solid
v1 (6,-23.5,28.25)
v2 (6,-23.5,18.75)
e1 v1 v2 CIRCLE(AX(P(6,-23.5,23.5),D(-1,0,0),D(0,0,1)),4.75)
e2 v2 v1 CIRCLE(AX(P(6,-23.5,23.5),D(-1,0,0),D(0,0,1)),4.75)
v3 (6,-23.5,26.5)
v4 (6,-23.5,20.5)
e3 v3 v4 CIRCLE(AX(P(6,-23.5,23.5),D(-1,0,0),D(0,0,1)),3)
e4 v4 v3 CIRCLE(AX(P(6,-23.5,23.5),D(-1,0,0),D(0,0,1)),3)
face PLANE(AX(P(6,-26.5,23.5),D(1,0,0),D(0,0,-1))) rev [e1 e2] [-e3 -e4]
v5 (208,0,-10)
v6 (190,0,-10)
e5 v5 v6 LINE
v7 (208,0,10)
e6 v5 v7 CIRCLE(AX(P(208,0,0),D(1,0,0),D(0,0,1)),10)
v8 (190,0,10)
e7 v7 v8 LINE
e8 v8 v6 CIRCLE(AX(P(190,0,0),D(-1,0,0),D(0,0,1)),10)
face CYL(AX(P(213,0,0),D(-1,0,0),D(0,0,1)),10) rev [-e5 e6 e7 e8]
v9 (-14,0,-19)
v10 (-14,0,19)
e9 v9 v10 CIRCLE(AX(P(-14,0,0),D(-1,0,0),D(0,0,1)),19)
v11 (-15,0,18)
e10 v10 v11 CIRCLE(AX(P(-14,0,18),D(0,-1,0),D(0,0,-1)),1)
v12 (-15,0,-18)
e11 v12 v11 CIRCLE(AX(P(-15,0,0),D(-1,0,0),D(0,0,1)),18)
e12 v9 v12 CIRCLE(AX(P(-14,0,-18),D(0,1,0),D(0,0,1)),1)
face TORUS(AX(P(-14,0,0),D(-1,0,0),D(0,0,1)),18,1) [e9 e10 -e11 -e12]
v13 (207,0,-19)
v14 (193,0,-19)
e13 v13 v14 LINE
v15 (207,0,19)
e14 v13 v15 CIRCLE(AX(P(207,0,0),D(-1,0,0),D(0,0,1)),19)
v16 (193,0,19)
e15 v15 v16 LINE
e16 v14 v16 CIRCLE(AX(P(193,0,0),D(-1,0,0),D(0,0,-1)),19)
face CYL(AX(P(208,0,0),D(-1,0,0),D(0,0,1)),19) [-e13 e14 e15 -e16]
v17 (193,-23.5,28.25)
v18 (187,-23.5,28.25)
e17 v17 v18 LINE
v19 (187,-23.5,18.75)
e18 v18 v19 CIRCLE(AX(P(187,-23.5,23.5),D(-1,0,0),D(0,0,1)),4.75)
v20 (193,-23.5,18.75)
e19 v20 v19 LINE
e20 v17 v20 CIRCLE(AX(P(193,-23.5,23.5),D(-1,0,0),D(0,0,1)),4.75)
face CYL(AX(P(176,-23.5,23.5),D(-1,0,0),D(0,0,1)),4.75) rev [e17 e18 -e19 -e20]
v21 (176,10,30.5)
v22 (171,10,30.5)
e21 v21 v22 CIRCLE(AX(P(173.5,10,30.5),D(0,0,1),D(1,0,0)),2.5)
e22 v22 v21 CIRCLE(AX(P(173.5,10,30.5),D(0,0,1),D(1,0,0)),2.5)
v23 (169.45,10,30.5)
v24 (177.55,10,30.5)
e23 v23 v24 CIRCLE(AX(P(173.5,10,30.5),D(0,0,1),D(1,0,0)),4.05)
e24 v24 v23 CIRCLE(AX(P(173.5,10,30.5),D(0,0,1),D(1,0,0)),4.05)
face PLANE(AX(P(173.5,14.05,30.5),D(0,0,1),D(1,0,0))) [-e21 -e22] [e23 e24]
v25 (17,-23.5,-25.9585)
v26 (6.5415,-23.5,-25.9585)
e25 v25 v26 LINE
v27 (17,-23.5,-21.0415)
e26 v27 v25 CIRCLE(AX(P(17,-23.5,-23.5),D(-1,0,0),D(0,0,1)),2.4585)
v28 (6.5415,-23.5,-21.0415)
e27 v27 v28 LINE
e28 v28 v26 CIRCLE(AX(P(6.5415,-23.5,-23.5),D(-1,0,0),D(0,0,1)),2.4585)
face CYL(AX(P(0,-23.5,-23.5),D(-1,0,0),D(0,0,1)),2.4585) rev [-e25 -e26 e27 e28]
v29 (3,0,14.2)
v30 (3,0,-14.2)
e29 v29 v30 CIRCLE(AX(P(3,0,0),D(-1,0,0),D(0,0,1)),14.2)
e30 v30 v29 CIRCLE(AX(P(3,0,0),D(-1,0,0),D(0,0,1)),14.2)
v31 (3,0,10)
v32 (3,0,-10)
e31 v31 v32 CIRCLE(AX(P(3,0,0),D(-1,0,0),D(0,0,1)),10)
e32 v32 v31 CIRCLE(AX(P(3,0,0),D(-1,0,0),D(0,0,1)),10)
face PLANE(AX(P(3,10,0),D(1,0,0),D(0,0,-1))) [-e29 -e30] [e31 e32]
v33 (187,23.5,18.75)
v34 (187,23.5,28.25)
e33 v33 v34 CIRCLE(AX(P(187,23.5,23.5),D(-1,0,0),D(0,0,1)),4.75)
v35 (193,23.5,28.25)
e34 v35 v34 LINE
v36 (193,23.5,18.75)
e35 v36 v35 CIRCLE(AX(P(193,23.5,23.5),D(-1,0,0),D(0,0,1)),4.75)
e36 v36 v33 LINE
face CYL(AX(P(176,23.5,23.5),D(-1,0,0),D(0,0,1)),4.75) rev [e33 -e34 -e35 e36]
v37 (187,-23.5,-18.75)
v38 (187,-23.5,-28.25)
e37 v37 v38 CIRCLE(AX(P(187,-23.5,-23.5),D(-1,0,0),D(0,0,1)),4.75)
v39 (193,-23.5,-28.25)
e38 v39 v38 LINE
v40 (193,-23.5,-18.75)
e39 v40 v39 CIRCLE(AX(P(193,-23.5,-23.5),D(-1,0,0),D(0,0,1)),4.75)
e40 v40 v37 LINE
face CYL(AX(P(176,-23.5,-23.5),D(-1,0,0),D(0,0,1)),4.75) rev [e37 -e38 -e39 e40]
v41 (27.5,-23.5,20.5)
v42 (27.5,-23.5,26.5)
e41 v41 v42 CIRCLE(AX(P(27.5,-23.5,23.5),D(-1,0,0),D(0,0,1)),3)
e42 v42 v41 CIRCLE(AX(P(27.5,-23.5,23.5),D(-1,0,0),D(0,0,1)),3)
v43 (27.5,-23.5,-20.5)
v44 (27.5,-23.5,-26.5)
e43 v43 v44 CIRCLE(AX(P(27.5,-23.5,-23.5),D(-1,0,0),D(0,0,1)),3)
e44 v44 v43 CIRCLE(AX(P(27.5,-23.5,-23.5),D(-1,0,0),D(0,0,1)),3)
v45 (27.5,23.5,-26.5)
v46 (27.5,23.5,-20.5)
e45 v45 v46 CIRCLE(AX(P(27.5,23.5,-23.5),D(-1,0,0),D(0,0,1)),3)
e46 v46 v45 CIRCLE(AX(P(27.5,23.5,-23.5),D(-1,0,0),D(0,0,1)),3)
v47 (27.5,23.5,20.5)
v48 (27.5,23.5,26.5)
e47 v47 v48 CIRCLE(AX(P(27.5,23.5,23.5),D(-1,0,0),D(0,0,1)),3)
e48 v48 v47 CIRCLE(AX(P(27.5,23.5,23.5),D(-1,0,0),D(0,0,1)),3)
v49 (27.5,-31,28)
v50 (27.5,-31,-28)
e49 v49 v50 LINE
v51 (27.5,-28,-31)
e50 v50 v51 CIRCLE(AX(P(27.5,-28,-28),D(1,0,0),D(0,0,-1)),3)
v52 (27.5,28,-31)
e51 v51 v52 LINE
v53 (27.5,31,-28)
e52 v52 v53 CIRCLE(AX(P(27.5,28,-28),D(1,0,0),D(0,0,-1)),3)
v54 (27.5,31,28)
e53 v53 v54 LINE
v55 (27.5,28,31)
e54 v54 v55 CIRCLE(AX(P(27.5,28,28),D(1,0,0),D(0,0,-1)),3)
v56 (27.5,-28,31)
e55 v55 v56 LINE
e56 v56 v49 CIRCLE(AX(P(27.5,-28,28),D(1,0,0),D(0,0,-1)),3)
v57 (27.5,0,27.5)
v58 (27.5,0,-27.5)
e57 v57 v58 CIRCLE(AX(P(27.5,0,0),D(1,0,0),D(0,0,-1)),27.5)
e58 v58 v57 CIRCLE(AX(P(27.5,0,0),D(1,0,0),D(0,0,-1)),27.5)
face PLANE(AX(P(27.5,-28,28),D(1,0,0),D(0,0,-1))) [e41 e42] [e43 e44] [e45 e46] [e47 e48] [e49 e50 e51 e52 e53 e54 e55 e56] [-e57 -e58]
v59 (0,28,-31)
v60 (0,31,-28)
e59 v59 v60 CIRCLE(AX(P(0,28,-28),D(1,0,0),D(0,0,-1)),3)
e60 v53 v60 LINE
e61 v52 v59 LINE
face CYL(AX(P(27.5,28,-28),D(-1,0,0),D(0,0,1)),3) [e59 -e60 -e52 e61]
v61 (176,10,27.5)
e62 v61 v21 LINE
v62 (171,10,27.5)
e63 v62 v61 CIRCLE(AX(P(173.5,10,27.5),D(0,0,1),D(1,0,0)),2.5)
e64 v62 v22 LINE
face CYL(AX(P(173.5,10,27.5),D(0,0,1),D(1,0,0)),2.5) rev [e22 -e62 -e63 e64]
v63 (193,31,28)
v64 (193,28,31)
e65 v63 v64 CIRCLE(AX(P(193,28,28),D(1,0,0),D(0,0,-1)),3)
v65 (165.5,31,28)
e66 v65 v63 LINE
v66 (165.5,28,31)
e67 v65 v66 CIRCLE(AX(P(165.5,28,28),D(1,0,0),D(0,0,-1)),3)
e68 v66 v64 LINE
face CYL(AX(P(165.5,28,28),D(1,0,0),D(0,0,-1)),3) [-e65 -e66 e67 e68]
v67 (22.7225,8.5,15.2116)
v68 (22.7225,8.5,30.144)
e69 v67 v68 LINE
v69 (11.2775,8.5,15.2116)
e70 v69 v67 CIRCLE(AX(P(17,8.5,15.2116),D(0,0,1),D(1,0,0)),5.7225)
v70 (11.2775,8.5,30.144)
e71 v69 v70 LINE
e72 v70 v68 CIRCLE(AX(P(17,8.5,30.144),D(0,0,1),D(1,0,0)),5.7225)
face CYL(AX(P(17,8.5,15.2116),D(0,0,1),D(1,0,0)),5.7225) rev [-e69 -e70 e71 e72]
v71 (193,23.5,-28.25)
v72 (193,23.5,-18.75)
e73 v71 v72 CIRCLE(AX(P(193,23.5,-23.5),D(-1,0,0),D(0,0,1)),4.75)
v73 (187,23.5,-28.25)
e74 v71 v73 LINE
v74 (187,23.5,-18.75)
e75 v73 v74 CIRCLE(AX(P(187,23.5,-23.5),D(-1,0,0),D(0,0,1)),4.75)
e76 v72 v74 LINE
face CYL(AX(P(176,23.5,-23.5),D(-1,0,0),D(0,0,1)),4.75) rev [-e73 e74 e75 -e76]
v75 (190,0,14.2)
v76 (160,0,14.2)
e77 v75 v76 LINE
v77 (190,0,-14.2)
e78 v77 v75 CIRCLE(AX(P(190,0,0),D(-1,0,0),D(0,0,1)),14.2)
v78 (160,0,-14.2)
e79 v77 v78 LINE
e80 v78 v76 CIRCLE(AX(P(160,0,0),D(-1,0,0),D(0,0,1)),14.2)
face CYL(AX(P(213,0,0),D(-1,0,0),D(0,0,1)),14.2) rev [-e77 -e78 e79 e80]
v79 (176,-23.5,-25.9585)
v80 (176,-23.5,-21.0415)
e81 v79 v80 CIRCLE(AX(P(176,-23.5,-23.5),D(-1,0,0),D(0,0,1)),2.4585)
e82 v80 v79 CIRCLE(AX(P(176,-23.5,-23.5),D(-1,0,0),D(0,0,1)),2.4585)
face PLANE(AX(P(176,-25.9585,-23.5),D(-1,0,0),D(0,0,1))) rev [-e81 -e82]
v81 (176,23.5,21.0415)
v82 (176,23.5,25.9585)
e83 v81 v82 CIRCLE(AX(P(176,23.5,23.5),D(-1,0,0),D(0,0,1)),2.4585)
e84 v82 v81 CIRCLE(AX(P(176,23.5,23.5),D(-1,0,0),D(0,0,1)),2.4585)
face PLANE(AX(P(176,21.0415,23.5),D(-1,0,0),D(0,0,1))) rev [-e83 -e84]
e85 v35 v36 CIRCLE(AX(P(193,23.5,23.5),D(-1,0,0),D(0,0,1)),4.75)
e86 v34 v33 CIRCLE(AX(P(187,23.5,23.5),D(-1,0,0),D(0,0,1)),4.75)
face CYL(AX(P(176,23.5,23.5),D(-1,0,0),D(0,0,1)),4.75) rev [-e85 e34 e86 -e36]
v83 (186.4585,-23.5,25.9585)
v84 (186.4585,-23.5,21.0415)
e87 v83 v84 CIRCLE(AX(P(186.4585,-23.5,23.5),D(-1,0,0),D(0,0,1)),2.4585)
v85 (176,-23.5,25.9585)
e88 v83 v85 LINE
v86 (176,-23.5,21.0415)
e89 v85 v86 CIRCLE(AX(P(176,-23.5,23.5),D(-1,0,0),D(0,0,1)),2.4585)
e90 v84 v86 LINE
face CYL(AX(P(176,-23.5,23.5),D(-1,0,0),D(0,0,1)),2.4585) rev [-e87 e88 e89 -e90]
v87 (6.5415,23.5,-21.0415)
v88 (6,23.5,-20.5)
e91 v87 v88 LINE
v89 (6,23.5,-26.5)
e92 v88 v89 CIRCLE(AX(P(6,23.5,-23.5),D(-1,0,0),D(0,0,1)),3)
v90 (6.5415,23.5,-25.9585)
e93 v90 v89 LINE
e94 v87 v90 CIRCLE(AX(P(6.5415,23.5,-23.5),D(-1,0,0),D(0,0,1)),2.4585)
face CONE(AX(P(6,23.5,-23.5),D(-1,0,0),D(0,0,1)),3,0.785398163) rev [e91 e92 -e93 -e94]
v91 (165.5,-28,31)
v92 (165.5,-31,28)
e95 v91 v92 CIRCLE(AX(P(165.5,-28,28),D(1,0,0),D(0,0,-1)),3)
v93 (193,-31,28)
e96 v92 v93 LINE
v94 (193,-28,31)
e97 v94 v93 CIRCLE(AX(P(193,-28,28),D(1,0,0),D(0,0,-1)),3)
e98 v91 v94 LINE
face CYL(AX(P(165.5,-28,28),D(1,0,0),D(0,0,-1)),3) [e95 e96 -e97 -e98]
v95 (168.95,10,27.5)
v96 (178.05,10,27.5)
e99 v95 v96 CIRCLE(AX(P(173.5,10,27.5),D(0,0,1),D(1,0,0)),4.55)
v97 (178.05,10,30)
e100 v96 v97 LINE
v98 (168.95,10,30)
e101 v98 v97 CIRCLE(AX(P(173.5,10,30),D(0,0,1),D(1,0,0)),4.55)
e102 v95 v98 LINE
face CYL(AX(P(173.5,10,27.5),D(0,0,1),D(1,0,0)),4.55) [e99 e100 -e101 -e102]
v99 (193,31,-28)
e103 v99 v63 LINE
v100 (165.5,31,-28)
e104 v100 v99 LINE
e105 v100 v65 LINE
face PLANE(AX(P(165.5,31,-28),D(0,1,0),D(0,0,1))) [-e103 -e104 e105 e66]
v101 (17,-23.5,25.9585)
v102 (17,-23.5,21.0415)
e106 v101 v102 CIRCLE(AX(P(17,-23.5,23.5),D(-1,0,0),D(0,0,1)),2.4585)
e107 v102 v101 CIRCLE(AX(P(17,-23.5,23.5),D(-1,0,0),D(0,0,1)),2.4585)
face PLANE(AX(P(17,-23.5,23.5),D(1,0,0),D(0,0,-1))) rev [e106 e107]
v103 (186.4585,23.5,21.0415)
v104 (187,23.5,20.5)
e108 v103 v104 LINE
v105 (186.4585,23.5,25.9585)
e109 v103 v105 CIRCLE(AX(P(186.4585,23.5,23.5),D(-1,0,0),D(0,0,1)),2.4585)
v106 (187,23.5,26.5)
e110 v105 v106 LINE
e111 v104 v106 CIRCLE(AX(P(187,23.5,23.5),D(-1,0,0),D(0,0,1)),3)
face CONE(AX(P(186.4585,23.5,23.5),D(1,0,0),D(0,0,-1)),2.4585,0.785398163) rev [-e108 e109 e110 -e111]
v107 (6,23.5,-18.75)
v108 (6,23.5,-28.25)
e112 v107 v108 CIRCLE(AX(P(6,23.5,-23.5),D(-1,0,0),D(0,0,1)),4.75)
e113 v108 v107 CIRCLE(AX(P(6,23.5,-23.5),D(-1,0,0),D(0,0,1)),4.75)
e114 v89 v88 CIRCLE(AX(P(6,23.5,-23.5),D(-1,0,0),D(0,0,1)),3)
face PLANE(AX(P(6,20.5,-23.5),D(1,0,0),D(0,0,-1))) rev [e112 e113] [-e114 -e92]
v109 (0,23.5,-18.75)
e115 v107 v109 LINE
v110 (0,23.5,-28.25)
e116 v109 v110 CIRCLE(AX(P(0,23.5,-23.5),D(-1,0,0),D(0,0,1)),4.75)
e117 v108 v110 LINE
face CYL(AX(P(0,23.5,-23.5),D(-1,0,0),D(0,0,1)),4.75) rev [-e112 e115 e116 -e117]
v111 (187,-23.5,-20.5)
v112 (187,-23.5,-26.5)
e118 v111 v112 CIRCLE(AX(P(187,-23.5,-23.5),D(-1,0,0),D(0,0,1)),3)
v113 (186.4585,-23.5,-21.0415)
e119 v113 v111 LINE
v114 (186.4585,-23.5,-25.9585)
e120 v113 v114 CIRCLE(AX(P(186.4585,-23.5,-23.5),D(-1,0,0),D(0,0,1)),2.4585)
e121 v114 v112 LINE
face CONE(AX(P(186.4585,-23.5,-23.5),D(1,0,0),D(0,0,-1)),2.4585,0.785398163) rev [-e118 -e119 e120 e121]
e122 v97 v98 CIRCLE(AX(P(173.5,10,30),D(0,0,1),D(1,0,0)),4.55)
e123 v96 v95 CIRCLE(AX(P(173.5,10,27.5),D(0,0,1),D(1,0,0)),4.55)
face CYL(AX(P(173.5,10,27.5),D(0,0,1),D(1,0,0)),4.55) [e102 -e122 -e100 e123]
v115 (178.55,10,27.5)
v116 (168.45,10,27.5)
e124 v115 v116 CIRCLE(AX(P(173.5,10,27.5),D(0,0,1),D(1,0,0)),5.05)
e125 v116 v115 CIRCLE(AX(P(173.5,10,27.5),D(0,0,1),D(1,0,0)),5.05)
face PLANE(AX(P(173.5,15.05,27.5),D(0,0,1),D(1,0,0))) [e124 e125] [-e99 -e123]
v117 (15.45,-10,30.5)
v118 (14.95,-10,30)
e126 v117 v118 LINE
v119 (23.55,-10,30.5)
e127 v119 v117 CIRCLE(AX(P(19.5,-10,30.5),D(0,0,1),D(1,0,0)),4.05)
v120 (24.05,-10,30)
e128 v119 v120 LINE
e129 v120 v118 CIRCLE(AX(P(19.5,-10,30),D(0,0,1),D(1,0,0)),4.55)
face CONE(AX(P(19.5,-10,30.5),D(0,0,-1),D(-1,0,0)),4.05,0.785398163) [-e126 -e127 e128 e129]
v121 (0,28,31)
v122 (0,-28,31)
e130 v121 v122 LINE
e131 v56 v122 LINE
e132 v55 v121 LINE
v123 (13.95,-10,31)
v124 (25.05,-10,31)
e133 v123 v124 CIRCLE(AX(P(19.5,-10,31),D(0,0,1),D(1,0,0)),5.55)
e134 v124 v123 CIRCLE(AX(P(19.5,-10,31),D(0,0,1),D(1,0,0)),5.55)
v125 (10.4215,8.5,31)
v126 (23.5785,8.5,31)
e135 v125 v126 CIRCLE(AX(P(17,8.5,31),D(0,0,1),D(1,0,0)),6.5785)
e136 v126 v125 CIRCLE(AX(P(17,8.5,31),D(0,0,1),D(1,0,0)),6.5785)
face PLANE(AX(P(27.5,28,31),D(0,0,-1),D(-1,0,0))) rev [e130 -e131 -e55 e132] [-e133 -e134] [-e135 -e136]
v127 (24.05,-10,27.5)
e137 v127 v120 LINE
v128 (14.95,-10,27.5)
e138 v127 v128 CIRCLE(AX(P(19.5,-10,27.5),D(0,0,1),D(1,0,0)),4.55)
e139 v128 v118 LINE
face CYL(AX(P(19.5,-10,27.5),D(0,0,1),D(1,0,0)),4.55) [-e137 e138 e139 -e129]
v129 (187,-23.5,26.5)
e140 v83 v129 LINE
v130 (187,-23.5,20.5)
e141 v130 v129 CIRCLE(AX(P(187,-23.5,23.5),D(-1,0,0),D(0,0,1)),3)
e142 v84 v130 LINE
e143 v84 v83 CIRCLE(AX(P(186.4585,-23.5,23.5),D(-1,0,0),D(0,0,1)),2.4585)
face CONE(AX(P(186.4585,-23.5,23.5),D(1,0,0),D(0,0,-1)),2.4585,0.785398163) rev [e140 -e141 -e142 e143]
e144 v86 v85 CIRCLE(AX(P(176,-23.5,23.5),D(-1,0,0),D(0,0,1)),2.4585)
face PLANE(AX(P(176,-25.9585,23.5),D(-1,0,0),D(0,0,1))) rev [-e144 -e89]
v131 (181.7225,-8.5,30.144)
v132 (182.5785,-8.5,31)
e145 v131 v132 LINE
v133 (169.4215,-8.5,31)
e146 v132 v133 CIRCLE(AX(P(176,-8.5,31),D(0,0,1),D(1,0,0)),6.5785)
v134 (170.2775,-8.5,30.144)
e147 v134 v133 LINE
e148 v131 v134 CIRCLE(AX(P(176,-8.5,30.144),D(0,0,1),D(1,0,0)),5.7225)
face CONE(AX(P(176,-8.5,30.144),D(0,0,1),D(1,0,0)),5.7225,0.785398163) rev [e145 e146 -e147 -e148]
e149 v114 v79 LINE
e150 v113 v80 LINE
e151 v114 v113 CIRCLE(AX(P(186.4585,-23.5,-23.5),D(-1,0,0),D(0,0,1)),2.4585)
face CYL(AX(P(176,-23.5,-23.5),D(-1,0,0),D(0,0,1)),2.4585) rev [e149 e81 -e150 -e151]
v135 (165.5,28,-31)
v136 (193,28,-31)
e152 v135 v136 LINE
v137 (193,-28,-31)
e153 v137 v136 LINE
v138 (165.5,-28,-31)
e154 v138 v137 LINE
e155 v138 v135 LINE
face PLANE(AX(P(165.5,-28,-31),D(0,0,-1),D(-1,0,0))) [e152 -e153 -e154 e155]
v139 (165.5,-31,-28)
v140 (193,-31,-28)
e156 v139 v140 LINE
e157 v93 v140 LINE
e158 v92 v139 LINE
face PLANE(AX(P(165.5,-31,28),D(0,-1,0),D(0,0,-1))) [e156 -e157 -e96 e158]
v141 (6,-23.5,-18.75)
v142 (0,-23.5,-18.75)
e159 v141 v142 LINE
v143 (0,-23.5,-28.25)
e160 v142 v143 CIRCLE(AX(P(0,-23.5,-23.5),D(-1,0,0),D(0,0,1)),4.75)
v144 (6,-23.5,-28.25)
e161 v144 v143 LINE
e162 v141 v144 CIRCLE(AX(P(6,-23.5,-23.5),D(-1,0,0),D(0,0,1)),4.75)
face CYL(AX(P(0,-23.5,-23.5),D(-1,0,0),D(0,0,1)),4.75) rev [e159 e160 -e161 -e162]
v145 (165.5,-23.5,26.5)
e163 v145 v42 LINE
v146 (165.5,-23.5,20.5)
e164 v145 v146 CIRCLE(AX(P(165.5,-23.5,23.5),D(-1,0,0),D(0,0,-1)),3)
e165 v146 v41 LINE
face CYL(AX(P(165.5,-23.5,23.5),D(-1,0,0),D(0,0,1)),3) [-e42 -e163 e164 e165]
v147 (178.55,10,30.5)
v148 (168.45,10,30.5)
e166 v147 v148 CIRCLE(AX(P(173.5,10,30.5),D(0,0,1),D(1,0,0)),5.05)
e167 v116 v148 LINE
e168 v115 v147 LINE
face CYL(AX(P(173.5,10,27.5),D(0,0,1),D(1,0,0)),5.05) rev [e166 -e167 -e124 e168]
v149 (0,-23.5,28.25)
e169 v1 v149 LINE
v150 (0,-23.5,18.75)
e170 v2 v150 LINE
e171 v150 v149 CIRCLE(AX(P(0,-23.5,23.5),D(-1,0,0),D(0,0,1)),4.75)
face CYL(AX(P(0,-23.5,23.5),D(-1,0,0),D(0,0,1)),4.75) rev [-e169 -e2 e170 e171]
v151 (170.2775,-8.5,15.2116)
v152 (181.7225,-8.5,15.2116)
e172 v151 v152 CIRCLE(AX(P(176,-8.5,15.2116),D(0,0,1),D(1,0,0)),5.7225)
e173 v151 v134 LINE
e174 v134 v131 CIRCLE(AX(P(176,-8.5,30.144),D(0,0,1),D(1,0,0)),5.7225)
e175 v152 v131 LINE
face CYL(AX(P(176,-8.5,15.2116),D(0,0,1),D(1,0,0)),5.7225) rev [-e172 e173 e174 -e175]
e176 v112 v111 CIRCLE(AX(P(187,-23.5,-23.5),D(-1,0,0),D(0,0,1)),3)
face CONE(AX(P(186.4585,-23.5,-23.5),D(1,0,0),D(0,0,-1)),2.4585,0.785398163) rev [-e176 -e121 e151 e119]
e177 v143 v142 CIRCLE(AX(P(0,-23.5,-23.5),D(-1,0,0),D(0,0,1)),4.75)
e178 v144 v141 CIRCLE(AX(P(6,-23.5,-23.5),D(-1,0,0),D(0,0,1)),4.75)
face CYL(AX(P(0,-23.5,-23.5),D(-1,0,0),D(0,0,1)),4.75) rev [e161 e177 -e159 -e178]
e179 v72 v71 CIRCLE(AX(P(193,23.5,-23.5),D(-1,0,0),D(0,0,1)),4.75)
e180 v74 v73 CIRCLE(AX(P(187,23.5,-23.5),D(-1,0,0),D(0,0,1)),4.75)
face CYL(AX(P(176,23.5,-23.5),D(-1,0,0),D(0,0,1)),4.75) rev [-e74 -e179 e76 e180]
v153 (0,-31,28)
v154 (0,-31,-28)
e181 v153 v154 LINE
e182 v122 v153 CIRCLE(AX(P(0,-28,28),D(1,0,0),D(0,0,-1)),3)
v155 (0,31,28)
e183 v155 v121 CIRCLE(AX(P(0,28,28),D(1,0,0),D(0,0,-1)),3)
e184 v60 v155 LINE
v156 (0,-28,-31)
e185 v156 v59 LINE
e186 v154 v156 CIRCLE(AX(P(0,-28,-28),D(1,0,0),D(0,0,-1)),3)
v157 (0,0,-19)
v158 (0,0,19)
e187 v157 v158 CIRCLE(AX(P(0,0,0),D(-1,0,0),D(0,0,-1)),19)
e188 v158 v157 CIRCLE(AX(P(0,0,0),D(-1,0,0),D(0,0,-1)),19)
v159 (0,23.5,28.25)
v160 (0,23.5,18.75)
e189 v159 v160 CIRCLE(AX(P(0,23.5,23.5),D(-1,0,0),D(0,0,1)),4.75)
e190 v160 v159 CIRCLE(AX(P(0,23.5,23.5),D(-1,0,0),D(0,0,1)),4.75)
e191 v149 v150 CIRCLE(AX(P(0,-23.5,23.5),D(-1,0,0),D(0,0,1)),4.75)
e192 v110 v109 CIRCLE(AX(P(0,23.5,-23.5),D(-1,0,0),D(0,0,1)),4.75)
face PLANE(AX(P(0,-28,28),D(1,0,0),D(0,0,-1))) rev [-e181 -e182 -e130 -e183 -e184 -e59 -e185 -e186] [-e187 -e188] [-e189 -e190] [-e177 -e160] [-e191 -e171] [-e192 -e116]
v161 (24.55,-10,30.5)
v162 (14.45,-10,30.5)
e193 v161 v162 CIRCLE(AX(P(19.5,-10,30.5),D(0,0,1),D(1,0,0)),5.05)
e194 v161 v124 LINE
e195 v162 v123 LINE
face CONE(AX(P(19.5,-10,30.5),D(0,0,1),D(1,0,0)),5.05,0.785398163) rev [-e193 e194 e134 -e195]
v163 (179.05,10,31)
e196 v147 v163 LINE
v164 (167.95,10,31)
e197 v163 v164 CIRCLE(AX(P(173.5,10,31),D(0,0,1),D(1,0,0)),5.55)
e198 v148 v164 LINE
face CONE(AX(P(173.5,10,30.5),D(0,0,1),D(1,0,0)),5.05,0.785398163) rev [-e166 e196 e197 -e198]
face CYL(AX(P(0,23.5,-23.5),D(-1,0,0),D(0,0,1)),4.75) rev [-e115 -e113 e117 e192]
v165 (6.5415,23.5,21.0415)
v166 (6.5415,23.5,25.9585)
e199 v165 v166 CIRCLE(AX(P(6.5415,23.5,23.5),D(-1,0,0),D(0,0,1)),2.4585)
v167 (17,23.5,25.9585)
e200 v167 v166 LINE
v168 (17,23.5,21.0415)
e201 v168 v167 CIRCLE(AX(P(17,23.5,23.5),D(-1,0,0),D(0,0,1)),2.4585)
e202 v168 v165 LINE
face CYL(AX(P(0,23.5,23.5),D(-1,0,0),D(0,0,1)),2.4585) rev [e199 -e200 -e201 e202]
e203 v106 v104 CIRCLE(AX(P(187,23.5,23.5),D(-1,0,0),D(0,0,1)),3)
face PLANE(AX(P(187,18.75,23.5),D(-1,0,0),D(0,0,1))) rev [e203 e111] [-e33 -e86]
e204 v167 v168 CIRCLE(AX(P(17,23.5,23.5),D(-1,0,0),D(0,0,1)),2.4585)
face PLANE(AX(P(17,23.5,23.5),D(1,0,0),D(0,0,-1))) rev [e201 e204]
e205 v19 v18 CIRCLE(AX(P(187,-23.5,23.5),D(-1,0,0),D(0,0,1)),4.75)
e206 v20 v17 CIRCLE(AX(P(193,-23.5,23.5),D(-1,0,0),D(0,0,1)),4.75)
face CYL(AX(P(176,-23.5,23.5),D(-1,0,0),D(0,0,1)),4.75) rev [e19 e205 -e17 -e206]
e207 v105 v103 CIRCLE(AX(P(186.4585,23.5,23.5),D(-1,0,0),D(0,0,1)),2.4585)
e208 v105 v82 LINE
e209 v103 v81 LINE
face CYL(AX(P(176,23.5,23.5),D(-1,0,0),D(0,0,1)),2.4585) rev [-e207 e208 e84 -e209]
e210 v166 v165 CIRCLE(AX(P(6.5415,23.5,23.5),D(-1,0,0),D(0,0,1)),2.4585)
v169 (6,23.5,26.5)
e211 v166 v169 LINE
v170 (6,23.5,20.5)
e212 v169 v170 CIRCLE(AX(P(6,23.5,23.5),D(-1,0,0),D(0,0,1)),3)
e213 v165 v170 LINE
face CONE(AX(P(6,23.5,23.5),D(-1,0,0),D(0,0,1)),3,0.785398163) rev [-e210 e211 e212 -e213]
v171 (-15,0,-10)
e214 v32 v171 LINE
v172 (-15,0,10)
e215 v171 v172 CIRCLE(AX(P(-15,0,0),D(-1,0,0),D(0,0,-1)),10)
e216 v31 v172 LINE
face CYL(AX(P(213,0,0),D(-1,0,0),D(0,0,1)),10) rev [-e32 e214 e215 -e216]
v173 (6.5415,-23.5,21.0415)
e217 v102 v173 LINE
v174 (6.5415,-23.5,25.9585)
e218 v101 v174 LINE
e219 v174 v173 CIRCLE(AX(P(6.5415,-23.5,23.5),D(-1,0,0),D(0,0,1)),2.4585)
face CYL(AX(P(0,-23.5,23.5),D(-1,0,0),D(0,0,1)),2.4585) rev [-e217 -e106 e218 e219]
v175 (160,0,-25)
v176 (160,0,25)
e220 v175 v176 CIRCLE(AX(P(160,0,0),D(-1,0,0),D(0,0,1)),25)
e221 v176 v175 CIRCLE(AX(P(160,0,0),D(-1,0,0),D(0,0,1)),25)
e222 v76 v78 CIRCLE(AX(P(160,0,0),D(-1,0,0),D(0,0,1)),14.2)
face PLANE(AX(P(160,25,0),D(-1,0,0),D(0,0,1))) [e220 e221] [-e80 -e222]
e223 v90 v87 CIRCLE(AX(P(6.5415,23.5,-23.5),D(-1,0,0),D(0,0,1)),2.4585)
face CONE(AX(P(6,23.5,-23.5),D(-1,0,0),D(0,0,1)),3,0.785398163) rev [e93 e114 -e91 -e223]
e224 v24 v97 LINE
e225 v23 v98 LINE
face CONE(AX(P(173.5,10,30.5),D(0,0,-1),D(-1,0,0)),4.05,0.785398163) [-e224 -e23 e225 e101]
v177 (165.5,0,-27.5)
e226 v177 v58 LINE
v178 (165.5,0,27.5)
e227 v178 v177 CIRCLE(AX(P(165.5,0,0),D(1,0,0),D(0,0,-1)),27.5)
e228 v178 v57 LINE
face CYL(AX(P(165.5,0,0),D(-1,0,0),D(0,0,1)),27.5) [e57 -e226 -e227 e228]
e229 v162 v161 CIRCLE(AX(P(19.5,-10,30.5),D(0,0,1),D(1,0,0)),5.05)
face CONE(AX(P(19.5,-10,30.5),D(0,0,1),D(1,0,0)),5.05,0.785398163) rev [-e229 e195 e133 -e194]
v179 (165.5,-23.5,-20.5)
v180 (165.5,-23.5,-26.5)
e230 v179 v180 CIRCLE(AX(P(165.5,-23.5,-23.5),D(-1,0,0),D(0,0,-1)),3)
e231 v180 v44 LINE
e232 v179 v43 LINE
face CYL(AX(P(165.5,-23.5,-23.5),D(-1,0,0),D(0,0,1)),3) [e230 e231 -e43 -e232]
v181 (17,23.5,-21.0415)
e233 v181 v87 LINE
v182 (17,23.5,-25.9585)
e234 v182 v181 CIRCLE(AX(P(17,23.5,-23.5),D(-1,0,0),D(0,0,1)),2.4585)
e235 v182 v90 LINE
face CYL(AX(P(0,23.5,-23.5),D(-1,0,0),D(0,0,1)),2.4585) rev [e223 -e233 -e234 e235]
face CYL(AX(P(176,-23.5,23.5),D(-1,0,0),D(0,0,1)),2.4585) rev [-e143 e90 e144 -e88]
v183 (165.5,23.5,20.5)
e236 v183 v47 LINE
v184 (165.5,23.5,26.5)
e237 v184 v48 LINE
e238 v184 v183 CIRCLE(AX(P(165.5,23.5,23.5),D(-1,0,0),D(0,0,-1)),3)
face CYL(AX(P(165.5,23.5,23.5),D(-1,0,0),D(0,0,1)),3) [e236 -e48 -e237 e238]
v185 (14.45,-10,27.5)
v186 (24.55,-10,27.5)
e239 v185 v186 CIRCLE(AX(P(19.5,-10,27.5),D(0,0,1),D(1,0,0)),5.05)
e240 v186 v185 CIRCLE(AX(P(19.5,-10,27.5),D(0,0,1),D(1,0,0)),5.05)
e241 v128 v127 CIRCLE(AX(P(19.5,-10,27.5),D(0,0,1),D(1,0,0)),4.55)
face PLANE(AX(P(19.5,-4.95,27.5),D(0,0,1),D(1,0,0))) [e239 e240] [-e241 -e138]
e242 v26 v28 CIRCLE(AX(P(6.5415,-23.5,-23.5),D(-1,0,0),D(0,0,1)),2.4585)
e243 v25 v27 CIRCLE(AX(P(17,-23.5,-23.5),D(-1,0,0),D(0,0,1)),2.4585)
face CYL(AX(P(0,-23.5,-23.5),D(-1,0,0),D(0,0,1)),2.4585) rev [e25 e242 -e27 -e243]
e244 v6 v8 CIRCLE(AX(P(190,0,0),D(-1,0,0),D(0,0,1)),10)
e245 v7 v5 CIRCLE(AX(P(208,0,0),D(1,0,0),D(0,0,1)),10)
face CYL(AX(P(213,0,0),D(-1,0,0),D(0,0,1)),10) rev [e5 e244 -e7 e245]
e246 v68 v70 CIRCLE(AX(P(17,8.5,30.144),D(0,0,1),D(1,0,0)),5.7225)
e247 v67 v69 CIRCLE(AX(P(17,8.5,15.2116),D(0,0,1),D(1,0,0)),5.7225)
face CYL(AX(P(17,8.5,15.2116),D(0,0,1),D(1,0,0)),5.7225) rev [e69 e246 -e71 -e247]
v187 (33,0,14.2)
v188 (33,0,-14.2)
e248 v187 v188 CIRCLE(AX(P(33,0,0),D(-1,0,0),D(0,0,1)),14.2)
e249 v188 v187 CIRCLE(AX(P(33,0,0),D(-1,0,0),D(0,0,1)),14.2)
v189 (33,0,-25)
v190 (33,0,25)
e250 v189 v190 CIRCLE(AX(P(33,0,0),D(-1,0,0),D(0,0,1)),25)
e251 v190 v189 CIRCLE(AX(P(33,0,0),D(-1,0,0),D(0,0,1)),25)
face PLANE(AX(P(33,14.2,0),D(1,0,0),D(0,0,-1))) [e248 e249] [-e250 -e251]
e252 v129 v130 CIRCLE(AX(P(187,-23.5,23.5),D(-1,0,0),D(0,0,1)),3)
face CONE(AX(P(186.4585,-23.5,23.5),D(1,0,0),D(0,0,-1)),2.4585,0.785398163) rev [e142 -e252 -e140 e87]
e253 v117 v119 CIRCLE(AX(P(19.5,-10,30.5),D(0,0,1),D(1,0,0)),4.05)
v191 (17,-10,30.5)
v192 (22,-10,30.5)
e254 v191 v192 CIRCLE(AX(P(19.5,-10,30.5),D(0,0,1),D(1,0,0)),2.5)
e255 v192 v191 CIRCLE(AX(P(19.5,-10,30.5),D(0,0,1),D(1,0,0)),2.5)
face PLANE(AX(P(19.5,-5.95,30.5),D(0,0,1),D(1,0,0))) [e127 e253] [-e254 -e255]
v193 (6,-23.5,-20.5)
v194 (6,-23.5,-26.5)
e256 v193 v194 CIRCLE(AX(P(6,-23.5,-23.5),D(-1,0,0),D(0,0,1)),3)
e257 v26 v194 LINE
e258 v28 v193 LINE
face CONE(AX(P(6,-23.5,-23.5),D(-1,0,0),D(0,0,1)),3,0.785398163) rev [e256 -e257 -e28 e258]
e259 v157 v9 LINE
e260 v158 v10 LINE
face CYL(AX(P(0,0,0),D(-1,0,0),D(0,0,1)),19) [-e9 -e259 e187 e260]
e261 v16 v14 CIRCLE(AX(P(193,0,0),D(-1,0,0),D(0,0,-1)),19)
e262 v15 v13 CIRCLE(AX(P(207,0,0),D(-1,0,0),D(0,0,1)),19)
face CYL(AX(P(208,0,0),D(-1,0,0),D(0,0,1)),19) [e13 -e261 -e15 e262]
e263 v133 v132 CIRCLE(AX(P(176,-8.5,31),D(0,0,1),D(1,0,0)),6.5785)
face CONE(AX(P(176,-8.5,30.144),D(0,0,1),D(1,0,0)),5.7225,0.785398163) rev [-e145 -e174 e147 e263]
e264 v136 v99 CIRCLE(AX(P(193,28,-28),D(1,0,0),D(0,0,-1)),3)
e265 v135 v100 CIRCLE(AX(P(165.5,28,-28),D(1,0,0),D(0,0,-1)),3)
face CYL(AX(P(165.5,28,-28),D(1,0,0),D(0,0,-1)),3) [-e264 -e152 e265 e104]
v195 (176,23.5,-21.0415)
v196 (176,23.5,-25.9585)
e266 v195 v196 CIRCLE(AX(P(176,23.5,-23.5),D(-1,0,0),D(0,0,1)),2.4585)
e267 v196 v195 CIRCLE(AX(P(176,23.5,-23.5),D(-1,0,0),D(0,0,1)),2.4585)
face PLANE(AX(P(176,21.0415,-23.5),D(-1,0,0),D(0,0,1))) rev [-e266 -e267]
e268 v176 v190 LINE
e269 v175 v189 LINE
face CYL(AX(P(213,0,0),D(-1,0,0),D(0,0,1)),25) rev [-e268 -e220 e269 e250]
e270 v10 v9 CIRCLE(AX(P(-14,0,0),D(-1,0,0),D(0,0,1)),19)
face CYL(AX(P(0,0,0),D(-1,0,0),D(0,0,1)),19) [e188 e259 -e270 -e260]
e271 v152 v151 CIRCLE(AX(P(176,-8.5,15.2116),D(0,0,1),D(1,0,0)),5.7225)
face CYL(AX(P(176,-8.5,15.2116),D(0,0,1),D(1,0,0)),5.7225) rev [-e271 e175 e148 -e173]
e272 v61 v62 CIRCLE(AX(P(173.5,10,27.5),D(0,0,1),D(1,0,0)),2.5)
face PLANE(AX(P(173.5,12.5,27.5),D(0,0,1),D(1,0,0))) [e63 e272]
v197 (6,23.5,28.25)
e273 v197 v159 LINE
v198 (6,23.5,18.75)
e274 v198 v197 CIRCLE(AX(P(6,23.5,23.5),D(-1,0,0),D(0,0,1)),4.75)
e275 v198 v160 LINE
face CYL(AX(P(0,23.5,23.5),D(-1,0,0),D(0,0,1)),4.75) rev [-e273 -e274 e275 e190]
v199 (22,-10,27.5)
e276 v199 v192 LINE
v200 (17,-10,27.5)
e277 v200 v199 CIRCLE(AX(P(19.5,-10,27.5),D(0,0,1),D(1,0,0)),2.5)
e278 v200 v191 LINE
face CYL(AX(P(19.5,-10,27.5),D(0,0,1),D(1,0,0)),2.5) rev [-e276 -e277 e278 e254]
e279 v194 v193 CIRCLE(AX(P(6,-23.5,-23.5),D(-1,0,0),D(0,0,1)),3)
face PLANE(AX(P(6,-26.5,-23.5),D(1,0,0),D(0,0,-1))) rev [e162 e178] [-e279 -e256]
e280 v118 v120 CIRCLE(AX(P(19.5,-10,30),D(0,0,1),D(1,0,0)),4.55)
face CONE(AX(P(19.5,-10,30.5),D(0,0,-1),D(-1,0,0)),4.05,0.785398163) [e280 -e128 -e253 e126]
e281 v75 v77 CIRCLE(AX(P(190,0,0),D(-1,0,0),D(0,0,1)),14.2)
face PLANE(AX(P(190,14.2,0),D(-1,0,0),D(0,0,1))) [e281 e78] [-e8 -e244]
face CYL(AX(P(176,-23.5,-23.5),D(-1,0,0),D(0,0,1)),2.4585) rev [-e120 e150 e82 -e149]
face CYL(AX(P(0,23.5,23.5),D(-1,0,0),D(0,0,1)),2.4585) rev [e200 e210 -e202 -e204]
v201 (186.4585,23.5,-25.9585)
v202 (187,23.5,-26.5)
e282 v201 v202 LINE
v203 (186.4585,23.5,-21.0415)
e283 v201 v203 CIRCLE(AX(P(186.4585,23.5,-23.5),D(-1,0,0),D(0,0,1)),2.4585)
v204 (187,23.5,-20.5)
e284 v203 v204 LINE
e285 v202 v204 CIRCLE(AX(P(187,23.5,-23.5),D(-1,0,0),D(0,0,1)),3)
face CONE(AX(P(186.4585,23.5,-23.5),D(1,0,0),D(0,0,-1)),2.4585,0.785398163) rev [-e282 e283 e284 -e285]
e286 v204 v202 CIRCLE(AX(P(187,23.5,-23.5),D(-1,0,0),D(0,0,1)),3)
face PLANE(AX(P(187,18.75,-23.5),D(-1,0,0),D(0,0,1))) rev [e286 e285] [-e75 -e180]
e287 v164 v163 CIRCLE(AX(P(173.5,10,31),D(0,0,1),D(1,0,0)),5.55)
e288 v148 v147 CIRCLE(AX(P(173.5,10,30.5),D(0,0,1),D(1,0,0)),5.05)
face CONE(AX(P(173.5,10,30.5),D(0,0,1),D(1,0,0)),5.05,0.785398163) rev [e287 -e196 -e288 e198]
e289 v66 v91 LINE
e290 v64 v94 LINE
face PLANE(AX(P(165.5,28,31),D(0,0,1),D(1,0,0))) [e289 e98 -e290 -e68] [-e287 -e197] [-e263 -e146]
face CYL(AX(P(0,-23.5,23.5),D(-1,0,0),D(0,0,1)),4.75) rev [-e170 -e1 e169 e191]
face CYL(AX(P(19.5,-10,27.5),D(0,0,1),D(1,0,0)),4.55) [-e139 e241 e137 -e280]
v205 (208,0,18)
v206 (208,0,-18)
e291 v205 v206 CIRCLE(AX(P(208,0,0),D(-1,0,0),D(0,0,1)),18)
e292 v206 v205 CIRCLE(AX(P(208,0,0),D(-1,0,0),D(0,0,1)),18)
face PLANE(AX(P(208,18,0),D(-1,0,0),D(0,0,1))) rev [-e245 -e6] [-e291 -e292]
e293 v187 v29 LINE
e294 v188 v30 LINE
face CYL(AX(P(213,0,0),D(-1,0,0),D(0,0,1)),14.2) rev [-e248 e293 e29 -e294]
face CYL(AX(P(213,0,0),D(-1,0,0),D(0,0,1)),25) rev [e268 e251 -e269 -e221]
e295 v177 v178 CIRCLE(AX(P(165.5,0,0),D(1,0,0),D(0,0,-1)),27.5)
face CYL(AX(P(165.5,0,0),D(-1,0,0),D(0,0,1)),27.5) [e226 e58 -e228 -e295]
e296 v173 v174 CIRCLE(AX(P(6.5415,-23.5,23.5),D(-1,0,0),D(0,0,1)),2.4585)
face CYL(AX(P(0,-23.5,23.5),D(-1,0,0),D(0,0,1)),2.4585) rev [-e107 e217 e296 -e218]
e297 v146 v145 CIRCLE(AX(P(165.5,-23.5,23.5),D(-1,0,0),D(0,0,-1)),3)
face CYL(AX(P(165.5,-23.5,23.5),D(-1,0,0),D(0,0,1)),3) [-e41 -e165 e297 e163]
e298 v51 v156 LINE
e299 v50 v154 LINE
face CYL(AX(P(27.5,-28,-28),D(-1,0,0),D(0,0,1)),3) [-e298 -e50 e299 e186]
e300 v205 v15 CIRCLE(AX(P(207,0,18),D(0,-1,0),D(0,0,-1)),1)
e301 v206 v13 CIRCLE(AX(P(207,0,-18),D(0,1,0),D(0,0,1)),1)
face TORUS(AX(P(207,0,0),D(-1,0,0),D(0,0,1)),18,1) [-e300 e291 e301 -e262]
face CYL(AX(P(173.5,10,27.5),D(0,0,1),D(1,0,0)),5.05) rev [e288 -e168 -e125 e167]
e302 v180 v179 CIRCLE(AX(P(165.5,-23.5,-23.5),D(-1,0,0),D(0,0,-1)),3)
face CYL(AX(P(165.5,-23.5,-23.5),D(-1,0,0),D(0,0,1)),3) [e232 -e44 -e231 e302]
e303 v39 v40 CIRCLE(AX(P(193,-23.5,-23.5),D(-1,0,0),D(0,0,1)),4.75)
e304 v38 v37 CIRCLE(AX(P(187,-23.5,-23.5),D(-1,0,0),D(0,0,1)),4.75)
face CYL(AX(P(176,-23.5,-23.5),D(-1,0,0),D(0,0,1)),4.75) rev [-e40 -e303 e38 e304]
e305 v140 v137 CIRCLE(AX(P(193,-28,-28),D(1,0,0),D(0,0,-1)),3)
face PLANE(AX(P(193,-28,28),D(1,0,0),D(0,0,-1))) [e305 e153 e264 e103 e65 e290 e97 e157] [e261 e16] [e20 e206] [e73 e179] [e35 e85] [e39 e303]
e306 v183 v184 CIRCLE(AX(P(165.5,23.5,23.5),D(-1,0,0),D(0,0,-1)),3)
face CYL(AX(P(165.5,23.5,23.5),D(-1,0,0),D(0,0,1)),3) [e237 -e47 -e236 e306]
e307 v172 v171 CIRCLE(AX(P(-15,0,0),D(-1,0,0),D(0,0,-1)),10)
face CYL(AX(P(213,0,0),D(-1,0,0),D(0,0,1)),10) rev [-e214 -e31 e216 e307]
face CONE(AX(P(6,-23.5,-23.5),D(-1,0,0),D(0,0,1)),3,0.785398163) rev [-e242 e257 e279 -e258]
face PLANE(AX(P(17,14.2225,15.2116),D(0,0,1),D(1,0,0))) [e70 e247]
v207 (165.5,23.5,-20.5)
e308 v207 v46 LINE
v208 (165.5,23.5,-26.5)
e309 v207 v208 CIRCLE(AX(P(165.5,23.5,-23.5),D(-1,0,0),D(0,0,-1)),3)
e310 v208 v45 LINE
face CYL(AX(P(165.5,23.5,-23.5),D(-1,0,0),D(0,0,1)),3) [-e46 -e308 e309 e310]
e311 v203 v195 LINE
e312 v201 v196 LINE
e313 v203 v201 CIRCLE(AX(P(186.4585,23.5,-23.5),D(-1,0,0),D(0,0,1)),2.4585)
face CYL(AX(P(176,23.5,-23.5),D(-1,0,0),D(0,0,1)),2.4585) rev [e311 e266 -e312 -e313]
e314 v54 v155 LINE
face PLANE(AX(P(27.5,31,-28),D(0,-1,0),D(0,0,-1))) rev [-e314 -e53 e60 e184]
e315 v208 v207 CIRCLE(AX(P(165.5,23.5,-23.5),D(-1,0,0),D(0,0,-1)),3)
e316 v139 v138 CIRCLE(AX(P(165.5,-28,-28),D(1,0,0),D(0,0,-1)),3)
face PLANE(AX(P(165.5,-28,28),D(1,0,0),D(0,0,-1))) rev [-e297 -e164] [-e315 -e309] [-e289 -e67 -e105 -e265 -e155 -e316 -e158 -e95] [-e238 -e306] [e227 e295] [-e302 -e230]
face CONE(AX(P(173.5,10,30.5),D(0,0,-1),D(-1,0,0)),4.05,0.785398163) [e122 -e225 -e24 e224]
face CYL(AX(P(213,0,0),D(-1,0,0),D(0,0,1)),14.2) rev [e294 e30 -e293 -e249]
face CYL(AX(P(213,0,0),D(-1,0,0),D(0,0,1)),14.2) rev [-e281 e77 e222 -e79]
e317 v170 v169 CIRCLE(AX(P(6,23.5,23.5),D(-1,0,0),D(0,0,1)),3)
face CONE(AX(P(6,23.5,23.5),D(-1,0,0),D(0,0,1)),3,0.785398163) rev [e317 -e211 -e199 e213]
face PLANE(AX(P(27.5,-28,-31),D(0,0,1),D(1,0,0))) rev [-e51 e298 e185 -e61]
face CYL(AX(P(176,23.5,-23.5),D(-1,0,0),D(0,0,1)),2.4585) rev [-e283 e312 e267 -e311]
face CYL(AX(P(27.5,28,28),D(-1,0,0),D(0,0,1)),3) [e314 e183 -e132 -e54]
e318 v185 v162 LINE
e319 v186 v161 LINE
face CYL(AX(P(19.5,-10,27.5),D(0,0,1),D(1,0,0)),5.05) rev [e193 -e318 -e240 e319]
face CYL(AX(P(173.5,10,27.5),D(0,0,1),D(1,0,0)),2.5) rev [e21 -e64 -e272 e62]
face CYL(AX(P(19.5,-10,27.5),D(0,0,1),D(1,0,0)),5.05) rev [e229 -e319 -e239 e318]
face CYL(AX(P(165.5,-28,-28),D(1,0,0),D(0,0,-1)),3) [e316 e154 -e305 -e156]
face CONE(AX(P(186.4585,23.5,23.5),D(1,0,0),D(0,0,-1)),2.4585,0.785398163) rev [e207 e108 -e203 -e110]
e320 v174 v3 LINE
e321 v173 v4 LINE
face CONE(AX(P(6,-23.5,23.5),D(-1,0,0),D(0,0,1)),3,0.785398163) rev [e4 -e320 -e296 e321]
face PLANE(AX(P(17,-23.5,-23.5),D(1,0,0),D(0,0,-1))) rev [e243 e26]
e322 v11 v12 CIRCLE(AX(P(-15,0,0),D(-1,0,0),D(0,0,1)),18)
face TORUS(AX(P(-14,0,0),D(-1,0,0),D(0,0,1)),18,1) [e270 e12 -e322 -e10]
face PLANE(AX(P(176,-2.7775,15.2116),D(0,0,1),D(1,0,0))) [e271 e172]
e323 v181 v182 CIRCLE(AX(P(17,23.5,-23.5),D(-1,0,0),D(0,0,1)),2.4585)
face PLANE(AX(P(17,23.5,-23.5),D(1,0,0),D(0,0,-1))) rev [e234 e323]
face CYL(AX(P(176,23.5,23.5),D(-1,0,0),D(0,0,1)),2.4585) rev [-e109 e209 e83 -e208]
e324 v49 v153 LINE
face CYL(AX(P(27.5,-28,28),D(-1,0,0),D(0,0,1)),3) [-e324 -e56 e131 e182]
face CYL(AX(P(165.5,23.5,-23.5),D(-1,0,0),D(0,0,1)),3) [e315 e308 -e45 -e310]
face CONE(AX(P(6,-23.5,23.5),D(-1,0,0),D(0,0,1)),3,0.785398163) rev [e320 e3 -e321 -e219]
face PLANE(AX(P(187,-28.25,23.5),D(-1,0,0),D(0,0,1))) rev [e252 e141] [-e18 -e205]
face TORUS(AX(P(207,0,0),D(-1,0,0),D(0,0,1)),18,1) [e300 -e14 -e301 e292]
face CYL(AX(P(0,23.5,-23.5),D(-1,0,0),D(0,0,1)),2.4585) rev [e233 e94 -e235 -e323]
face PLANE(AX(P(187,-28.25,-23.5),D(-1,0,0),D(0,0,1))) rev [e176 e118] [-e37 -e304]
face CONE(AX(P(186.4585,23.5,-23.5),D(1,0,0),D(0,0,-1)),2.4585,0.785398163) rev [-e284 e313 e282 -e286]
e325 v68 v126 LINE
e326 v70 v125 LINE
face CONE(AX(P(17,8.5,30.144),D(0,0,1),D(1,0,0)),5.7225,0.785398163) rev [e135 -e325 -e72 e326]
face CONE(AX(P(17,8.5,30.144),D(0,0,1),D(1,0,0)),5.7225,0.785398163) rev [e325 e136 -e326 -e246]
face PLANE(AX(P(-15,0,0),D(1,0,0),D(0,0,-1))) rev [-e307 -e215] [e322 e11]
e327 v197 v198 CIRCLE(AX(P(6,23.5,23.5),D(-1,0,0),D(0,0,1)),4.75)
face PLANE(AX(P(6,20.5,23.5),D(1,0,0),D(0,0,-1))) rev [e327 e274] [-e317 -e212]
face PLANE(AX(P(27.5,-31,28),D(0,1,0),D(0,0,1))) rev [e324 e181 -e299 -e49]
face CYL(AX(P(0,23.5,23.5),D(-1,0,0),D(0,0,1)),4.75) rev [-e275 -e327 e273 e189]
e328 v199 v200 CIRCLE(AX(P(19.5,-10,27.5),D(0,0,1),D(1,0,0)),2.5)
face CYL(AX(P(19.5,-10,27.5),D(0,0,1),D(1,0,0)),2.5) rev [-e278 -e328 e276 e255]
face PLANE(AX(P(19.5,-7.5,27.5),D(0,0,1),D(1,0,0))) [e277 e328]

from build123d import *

# Parameters (mm, degrees)
BOSS_EXTRUDE1_DEPTH  = 27.5
SKETCH2_R            = 27.5
BOSS_EXTRUDE2_DEPTH  = 138
BOSS_EXTRUDE3_START  = -27.5
BOSS_EXTRUDE3_DEPTH  = 27.5
LPATTERN1_COUNT      = 2
LPATTERN1_PITCH      = 47
LPATTERN1_COUNT_DIR2 = 2
LPATTERN1_PITCH_DIR2 = 47
LPATTERN2_COUNT      = 2
LPATTERN2_PITCH      = 47
LPATTERN2_COUNT_DIR2 = 2
LPATTERN2_PITCH_DIR2 = 47
SKETCH8_W            = 138
SKETCH8_H            = 3
LPATTERN3_COUNT      = 2
LPATTERN3_PITCH      = 47
LPATTERN3_COUNT_DIR2 = 2
LPATTERN3_PITCH_DIR2 = 47


with BuildPart() as part:
    # Sketch1 → Boss-Extrude1 (new body)
    with BuildSketch(Plane(origin=(0, 0, 0), x_dir=(0, 0, -1), z_dir=(1, 0, 0))):
        with BuildLine():
            Line((-28, -31), (28, -31))
            ThreePointArc((28, -31), (30.121320344, -30.121320344), (31, -28))
            Line((31, -28), (31, 28))
            ThreePointArc((31, 28), (30.121320344, 30.121320344), (28, 31))
            Line((28, 31), (-28, 31))
            ThreePointArc((-28, 31), (-30.121320344, 30.121320344), (-31, 28))
            Line((-31, 28), (-31, -28))
            ThreePointArc((-31, -28), (-30.121320344, -30.121320344), (-28, -31))
        make_face()
    extrude(amount=BOSS_EXTRUDE1_DEPTH)

    # Sketch2 → Boss-Extrude2 (add)
    with BuildSketch(Plane(origin=(27.5, 0, 0), x_dir=(0, 0, -1), z_dir=(1, 0, 0))):
        Circle(SKETCH2_R)
    extrude(amount=BOSS_EXTRUDE2_DEPTH)

    # Sketch3 → Boss-Extrude3 (add)
    with BuildSketch(Plane(origin=(193, 0, 0), x_dir=(0, 0, -1), z_dir=(1, 0, 0)).offset(BOSS_EXTRUDE3_START)):
        with BuildLine():
            Line((-28, -31), (28, -31))
            ThreePointArc((28, -31), (30.121320344, -30.121320344), (31, -28))
            Line((31, -28), (31, 28))
            ThreePointArc((31, 28), (30.121320344, 30.121320344), (28, 31))
            Line((28, 31), (-28, 31))
            ThreePointArc((-28, 31), (-30.121320344, 30.121320344), (-31, 28))
            Line((-31, 28), (-31, -28))
            ThreePointArc((-31, -28), (-30.121320344, -30.121320344), (-28, -31))
        make_face()
    extrude(amount=BOSS_EXTRUDE3_DEPTH)

    # Sketch4 → Cut-Revolve1 (revolve, cut)
    with BuildSketch(Plane.XY.offset(23.5), mode=Mode.PRIVATE) as cut_revolve1_sk:
        Polygon((17, -23.5), (17, -25.9585), (6.5415, -25.9585), (6, -26.5), (6, -28.25), (0, -28.25), (0, -23.5), align=None)
    cut_revolve1 = revolve(cut_revolve1_sk.sketch.rotate(Axis((0, -23.5, 23.5), (1, 0, 0)), 270), axis=Axis((0, -23.5, 23.5), (1, 0, 0)), mode=Mode.SUBTRACT)

    # LPattern1: Cut-Revolve1 2 × 2
    with Locations(*[(0, j * LPATTERN1_PITCH_DIR2, -i * LPATTERN1_PITCH) for i in range(LPATTERN1_COUNT) for j in range(LPATTERN1_COUNT_DIR2) if (i, j) != (0, 0)]):
        add(cut_revolve1, mode=Mode.SUBTRACT)

    # Sketch6 → Cut-Revolve2 (revolve, cut)
    with BuildSketch(Plane.XY.offset(23.5), mode=Mode.PRIVATE) as cut_revolve2_sk:
        Polygon((193, -23.5), (193, -28.25), (187, -28.25), (187, -26.5), (186.4585, -25.9585), (176, -25.9585), (176, -23.5), align=None)
    cut_revolve2 = revolve(cut_revolve2_sk.sketch.rotate(Axis((176, -23.5, 23.5), (1, 0, 0)), 270), axis=Axis((176, -23.5, 23.5), (1, 0, 0)), mode=Mode.SUBTRACT)

    # LPattern2: Cut-Revolve2 2 × 2
    with Locations(*[(0, j * LPATTERN2_PITCH_DIR2, -i * LPATTERN2_PITCH) for i in range(LPATTERN2_COUNT) for j in range(LPATTERN2_COUNT_DIR2) if (i, j) != (0, 0)]):
        add(cut_revolve2, mode=Mode.SUBTRACT)

    # Sketch8 → Revolve1 (revolve)
    with BuildSketch(Plane.XY.offset(23.5), mode=Mode.PRIVATE) as revolve1_sk:
        with Locations((96.5, -22)):
            Rectangle(SKETCH8_W, SKETCH8_H)
    revolve1 = revolve(revolve1_sk.sketch.rotate(Axis((165.5, -23.5, 23.5), (-1, 0, 0)), 270), axis=Axis((165.5, -23.5, 23.5), (-1, 0, 0)))

    # LPattern3: Revolve1 2 × 2
    with Locations(*[(0, j * LPATTERN3_PITCH_DIR2, -i * LPATTERN3_PITCH) for i in range(LPATTERN3_COUNT) for j in range(LPATTERN3_COUNT_DIR2) if (i, j) != (0, 0)]):
        add(revolve1)

    # Sketch10 → Revolve2 (revolve)
    with BuildSketch(Plane.XY, mode=Mode.PRIVATE) as revolve2_sk:
        with BuildLine():
            Line((165.5, 0), (165.5, 19))
            Line((165.5, 19), (207, 19))
            ThreePointArc((207, 19), (207.707106781, 18.707106781), (208, 18))
            Line((208, 18), (208, 0))
            Line((208, 0), (165.5, 0))
        make_face()
    revolve(revolve2_sk.sketch.rotate(Axis((208, 0, 0), (-1, 0, 0)), 270), axis=Axis((208, 0, 0), (-1, 0, 0)))

    # Sketch11 → Cut-Revolve3 (revolve, cut)
    with BuildSketch(Plane(origin=(17, 0, 0), x_dir=(0, 0, -1), z_dir=(1, 0, 0)), mode=Mode.PRIVATE) as cut_revolve3_sk:
        Polygon((-31, 8.5), (-31, 15.0785), (-30.144, 14.2225), (-15.2116, 14.2225), (-15.2116, 8.5), align=None)
    revolve(cut_revolve3_sk.sketch.rotate(Axis((17, 8.5, 15.2116), (0, 0, 1)), 270), axis=Axis((17, 8.5, 15.2116), (0, 0, 1)), mode=Mode.SUBTRACT)

    # Sketch12 → Cut-Revolve4 (revolve, cut)
    with BuildSketch(Plane(origin=(176, 0, 0), x_dir=(0, 0, -1), z_dir=(1, 0, 0)), mode=Mode.PRIVATE) as cut_revolve4_sk:
        Polygon((-31, -8.5), (-31, -1.9215), (-30.144, -2.7775), (-15.2116, -2.7775), (-15.2116, -8.5), align=None)
    revolve(cut_revolve4_sk.sketch.rotate(Axis((176, -8.5, 15.2116), (0, 0, 1)), 270), axis=Axis((176, -8.5, 15.2116), (0, 0, 1)), mode=Mode.SUBTRACT)

    # Sketch13 → Cut-Revolve5 (revolve, cut)
    with BuildSketch(Plane(origin=(19.5, 0, 0), x_dir=(0, 0, -1), z_dir=(1, 0, 0)), mode=Mode.PRIVATE) as cut_revolve5_sk:
        Polygon((-31, -10), (-31, -4.45), (-30.5, -4.95), (-27.5, -4.95), (-27.5, -5.45), (-30, -5.45), (-30.5, -5.95), (-30.5, -7.5), (-27.5, -7.5), (-27.5, -10), align=None)
    revolve(cut_revolve5_sk.sketch.rotate(Axis((19.5, -10, 27.5), (0, 0, 1)), 270), axis=Axis((19.5, -10, 27.5), (0, 0, 1)), mode=Mode.SUBTRACT)

    # Sketch14 → Cut-Revolve6 (revolve, cut)
    with BuildSketch(Plane(origin=(173.5, 0, 0), x_dir=(0, 0, -1), z_dir=(1, 0, 0)), mode=Mode.PRIVATE) as cut_revolve6_sk:
        Polygon((-31, 10), (-31, 15.55), (-30.5, 15.05), (-27.5, 15.05), (-27.5, 14.55), (-30, 14.55), (-30.5, 14.05), (-30.5, 12.5), (-27.5, 12.5), (-27.5, 10), align=None)
    revolve(cut_revolve6_sk.sketch.rotate(Axis((173.5, 10, 27.5), (0, 0, 1)), 270), axis=Axis((173.5, 10, 27.5), (0, 0, 1)), mode=Mode.SUBTRACT)

    # Sketch15 → Revolve3 (revolve)
    with BuildSketch(Plane.XY, mode=Mode.PRIVATE) as revolve3_sk:
        with BuildLine():
            Line((-15, 0), (-15, 18))
            ThreePointArc((-15, 18), (-14.707106781, 18.707106781), (-14, 19))
            Line((-14, 19), (0, 19))
            Line((0, 19), (0, 0))
            Line((0, 0), (-15, 0))
        make_face()
    revolve(revolve3_sk.sketch.rotate(Axis((0, 0, 0), (-1, 0, 0)), 270), axis=Axis((0, 0, 0), (-1, 0, 0)))

    # Sketch16 → Cut-Revolve7 (revolve, cut)
    with BuildSketch(Plane.XY, mode=Mode.PRIVATE) as cut_revolve7_sk:
        Polygon((-20, 0), (-20, 10), (3, 10), (3, 14.2), (33, 14.2), (33, 25), (160, 25), (160, 14.2), (190, 14.2), (190, 10), (213, 10), (213, 0), align=None)
    revolve(cut_revolve7_sk.sketch.rotate(Axis((213, 0, 0), (-1, 0, 0)), 270), axis=Axis((213, 0, 0), (-1, 0, 0)), mode=Mode.SUBTRACT)


solid = part.part
